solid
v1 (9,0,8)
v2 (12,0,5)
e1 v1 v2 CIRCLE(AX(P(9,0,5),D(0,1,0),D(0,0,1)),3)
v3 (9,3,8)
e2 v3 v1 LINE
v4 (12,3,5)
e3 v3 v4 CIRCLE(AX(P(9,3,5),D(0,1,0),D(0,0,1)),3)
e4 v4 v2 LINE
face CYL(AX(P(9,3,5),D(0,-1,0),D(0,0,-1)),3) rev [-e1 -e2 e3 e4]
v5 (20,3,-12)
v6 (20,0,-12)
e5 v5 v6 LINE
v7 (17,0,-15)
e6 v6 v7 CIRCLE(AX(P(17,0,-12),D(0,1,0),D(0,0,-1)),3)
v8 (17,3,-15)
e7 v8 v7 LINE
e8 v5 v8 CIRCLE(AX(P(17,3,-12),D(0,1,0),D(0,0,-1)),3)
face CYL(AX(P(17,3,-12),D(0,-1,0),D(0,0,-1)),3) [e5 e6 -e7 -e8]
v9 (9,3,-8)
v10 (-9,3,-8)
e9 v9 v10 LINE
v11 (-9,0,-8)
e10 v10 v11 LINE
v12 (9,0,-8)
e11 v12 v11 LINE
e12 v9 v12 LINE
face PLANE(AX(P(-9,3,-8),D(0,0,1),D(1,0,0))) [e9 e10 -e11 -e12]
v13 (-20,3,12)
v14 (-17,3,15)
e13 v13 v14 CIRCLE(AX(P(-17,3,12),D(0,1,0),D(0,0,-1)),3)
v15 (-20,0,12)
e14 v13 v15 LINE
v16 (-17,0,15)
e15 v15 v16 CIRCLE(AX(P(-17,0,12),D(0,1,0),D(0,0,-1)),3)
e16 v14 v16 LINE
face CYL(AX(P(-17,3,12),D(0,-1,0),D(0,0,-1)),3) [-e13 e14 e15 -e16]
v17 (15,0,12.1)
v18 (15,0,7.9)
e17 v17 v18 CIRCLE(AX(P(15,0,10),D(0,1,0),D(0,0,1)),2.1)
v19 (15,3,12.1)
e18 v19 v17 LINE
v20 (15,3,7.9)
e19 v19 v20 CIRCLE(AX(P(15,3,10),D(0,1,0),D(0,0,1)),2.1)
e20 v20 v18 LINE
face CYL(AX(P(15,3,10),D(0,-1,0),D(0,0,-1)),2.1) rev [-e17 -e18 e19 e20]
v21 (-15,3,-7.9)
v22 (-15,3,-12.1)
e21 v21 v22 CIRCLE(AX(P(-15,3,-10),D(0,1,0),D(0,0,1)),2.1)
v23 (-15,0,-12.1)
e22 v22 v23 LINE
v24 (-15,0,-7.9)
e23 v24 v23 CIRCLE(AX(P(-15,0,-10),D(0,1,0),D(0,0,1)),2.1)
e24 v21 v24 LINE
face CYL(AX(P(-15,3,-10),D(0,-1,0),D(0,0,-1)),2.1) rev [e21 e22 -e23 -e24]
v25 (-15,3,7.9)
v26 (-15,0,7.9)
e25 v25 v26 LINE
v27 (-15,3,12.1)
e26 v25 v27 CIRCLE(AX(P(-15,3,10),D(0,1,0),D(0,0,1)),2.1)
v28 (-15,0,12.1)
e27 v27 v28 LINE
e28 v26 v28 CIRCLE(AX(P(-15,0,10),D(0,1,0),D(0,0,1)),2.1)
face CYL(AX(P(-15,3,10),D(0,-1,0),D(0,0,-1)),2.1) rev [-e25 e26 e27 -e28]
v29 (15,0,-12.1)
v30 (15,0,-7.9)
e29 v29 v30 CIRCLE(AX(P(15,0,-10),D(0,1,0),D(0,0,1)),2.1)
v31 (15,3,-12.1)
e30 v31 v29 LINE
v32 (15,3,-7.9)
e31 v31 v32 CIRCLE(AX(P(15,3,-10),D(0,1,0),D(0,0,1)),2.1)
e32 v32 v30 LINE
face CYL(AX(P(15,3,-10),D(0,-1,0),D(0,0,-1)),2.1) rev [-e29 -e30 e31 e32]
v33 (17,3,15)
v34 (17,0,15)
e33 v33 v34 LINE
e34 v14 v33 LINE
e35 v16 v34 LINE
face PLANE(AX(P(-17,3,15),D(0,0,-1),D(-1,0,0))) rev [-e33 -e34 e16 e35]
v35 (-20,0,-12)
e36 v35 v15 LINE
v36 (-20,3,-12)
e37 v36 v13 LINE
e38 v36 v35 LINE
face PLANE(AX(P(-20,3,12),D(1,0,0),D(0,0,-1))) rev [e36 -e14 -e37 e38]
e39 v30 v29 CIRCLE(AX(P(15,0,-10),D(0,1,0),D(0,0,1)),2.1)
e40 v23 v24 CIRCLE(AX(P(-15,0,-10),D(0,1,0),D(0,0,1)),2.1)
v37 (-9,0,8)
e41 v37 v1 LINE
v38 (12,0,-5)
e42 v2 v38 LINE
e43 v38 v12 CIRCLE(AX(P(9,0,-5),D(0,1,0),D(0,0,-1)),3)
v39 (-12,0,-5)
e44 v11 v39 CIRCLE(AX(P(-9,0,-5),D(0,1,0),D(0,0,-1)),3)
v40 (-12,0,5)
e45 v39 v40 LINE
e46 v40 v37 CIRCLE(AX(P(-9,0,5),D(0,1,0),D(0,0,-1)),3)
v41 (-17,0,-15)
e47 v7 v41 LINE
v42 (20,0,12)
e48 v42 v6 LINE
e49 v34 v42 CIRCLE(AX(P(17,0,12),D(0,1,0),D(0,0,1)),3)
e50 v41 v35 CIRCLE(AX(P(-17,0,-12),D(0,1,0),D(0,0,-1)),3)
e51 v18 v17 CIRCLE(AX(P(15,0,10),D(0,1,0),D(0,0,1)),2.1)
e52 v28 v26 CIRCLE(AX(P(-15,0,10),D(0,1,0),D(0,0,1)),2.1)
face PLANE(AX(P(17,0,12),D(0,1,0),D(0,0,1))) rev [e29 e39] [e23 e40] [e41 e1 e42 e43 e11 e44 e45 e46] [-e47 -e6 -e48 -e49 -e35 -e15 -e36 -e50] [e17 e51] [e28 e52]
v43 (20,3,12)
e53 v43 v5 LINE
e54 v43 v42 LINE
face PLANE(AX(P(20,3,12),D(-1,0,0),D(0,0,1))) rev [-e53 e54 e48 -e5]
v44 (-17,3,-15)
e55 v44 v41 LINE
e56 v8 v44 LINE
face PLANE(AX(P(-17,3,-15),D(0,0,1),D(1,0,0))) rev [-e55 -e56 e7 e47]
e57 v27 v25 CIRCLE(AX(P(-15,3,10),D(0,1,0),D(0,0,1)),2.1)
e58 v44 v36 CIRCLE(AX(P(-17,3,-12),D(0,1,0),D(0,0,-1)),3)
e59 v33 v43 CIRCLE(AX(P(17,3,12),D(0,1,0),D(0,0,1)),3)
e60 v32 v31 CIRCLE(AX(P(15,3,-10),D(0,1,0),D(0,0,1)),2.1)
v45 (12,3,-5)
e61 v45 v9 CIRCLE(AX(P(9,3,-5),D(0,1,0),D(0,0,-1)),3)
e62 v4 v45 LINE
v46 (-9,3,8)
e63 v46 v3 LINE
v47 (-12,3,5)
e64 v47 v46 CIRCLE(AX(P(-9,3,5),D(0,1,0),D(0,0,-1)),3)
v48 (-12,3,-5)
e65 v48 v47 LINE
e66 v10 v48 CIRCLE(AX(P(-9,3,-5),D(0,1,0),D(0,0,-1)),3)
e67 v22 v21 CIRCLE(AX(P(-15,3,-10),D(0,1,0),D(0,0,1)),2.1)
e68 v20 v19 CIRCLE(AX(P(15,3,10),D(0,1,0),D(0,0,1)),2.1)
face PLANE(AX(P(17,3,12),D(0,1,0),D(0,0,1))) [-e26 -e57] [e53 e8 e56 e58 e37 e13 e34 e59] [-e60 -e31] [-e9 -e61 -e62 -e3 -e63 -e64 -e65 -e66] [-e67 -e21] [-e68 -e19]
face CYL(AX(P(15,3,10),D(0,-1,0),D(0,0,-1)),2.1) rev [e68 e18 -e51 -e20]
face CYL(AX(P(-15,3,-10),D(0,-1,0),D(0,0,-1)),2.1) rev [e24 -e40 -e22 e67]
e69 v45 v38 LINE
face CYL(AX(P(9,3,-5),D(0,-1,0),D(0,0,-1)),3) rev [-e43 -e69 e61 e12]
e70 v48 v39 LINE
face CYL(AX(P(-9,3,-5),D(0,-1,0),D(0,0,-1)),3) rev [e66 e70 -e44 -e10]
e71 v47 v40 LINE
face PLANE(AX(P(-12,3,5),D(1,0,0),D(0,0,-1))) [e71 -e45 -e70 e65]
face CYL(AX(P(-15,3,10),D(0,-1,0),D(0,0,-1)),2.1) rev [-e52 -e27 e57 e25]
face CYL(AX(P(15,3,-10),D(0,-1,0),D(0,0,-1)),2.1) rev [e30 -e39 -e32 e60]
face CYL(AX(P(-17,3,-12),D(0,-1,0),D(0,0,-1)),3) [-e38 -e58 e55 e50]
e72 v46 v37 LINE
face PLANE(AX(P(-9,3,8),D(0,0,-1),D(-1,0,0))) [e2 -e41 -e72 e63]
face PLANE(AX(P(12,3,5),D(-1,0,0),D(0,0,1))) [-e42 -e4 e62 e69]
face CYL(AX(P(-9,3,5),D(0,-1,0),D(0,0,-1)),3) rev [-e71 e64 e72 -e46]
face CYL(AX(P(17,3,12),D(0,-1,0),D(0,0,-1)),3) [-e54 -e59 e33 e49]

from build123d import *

# Parameters (mm, degrees)
SKETCH_1_R      = 2.1
EXTRUDE_1_DEPTH = 3


with BuildPart() as part:
    # 草图1 → 凸台-拉伸1 (new body)
    with BuildSketch(Plane(origin=(0, 0, 0), x_dir=(1, 0, 0), z_dir=(0, 1, 0))):
        with BuildLine():
            Line((-17, -15), (17, -15))
            ThreePointArc((17, -15), (19.121320344, -14.121320344), (20, -12))
            Line((20, -12), (20, 12))
            ThreePointArc((20, 12), (19.121320344, 14.121320344), (17, 15))
            Line((17, 15), (-17, 15))
            ThreePointArc((-17, 15), (-19.121320344, 14.121320344), (-20, 12))
            Line((-20, 12), (-20, -12))
            ThreePointArc((-20, -12), (-19.121320344, -14.121320344), (-17, -15))
        make_face()
        with Locations(Location((-15, 10, 0), (0, 0, 270))):
            Circle(SKETCH_1_R, mode=Mode.SUBTRACT)
        with Locations(Location((15, 10, 0), (0, 0, 270))):
            Circle(SKETCH_1_R, mode=Mode.SUBTRACT)
        with Locations(Location((-15, -10, 0), (0, 0, 270))):
            Circle(SKETCH_1_R, mode=Mode.SUBTRACT)
        with Locations(Location((15, -10, 0), (0, 0, 270))):
            Circle(SKETCH_1_R, mode=Mode.SUBTRACT)
        with BuildLine():
            Line((-9, -8), (9, -8))
            ThreePointArc((9, -8), (11.121320344, -7.121320344), (12, -5))
            Line((12, -5), (12, 5))
            ThreePointArc((12, 5), (11.121320344, 7.121320344), (9, 8))
            Line((9, 8), (-9, 8))
            ThreePointArc((-9, 8), (-11.121320344, 7.121320344), (-12, 5))
            Line((-12, 5), (-12, -5))
            ThreePointArc((-12, -5), (-11.121320344, -7.121320344), (-9, -8))
        make_face(mode=Mode.SUBTRACT)
    extrude(amount=EXTRUDE_1_DEPTH)


solid = part.part
